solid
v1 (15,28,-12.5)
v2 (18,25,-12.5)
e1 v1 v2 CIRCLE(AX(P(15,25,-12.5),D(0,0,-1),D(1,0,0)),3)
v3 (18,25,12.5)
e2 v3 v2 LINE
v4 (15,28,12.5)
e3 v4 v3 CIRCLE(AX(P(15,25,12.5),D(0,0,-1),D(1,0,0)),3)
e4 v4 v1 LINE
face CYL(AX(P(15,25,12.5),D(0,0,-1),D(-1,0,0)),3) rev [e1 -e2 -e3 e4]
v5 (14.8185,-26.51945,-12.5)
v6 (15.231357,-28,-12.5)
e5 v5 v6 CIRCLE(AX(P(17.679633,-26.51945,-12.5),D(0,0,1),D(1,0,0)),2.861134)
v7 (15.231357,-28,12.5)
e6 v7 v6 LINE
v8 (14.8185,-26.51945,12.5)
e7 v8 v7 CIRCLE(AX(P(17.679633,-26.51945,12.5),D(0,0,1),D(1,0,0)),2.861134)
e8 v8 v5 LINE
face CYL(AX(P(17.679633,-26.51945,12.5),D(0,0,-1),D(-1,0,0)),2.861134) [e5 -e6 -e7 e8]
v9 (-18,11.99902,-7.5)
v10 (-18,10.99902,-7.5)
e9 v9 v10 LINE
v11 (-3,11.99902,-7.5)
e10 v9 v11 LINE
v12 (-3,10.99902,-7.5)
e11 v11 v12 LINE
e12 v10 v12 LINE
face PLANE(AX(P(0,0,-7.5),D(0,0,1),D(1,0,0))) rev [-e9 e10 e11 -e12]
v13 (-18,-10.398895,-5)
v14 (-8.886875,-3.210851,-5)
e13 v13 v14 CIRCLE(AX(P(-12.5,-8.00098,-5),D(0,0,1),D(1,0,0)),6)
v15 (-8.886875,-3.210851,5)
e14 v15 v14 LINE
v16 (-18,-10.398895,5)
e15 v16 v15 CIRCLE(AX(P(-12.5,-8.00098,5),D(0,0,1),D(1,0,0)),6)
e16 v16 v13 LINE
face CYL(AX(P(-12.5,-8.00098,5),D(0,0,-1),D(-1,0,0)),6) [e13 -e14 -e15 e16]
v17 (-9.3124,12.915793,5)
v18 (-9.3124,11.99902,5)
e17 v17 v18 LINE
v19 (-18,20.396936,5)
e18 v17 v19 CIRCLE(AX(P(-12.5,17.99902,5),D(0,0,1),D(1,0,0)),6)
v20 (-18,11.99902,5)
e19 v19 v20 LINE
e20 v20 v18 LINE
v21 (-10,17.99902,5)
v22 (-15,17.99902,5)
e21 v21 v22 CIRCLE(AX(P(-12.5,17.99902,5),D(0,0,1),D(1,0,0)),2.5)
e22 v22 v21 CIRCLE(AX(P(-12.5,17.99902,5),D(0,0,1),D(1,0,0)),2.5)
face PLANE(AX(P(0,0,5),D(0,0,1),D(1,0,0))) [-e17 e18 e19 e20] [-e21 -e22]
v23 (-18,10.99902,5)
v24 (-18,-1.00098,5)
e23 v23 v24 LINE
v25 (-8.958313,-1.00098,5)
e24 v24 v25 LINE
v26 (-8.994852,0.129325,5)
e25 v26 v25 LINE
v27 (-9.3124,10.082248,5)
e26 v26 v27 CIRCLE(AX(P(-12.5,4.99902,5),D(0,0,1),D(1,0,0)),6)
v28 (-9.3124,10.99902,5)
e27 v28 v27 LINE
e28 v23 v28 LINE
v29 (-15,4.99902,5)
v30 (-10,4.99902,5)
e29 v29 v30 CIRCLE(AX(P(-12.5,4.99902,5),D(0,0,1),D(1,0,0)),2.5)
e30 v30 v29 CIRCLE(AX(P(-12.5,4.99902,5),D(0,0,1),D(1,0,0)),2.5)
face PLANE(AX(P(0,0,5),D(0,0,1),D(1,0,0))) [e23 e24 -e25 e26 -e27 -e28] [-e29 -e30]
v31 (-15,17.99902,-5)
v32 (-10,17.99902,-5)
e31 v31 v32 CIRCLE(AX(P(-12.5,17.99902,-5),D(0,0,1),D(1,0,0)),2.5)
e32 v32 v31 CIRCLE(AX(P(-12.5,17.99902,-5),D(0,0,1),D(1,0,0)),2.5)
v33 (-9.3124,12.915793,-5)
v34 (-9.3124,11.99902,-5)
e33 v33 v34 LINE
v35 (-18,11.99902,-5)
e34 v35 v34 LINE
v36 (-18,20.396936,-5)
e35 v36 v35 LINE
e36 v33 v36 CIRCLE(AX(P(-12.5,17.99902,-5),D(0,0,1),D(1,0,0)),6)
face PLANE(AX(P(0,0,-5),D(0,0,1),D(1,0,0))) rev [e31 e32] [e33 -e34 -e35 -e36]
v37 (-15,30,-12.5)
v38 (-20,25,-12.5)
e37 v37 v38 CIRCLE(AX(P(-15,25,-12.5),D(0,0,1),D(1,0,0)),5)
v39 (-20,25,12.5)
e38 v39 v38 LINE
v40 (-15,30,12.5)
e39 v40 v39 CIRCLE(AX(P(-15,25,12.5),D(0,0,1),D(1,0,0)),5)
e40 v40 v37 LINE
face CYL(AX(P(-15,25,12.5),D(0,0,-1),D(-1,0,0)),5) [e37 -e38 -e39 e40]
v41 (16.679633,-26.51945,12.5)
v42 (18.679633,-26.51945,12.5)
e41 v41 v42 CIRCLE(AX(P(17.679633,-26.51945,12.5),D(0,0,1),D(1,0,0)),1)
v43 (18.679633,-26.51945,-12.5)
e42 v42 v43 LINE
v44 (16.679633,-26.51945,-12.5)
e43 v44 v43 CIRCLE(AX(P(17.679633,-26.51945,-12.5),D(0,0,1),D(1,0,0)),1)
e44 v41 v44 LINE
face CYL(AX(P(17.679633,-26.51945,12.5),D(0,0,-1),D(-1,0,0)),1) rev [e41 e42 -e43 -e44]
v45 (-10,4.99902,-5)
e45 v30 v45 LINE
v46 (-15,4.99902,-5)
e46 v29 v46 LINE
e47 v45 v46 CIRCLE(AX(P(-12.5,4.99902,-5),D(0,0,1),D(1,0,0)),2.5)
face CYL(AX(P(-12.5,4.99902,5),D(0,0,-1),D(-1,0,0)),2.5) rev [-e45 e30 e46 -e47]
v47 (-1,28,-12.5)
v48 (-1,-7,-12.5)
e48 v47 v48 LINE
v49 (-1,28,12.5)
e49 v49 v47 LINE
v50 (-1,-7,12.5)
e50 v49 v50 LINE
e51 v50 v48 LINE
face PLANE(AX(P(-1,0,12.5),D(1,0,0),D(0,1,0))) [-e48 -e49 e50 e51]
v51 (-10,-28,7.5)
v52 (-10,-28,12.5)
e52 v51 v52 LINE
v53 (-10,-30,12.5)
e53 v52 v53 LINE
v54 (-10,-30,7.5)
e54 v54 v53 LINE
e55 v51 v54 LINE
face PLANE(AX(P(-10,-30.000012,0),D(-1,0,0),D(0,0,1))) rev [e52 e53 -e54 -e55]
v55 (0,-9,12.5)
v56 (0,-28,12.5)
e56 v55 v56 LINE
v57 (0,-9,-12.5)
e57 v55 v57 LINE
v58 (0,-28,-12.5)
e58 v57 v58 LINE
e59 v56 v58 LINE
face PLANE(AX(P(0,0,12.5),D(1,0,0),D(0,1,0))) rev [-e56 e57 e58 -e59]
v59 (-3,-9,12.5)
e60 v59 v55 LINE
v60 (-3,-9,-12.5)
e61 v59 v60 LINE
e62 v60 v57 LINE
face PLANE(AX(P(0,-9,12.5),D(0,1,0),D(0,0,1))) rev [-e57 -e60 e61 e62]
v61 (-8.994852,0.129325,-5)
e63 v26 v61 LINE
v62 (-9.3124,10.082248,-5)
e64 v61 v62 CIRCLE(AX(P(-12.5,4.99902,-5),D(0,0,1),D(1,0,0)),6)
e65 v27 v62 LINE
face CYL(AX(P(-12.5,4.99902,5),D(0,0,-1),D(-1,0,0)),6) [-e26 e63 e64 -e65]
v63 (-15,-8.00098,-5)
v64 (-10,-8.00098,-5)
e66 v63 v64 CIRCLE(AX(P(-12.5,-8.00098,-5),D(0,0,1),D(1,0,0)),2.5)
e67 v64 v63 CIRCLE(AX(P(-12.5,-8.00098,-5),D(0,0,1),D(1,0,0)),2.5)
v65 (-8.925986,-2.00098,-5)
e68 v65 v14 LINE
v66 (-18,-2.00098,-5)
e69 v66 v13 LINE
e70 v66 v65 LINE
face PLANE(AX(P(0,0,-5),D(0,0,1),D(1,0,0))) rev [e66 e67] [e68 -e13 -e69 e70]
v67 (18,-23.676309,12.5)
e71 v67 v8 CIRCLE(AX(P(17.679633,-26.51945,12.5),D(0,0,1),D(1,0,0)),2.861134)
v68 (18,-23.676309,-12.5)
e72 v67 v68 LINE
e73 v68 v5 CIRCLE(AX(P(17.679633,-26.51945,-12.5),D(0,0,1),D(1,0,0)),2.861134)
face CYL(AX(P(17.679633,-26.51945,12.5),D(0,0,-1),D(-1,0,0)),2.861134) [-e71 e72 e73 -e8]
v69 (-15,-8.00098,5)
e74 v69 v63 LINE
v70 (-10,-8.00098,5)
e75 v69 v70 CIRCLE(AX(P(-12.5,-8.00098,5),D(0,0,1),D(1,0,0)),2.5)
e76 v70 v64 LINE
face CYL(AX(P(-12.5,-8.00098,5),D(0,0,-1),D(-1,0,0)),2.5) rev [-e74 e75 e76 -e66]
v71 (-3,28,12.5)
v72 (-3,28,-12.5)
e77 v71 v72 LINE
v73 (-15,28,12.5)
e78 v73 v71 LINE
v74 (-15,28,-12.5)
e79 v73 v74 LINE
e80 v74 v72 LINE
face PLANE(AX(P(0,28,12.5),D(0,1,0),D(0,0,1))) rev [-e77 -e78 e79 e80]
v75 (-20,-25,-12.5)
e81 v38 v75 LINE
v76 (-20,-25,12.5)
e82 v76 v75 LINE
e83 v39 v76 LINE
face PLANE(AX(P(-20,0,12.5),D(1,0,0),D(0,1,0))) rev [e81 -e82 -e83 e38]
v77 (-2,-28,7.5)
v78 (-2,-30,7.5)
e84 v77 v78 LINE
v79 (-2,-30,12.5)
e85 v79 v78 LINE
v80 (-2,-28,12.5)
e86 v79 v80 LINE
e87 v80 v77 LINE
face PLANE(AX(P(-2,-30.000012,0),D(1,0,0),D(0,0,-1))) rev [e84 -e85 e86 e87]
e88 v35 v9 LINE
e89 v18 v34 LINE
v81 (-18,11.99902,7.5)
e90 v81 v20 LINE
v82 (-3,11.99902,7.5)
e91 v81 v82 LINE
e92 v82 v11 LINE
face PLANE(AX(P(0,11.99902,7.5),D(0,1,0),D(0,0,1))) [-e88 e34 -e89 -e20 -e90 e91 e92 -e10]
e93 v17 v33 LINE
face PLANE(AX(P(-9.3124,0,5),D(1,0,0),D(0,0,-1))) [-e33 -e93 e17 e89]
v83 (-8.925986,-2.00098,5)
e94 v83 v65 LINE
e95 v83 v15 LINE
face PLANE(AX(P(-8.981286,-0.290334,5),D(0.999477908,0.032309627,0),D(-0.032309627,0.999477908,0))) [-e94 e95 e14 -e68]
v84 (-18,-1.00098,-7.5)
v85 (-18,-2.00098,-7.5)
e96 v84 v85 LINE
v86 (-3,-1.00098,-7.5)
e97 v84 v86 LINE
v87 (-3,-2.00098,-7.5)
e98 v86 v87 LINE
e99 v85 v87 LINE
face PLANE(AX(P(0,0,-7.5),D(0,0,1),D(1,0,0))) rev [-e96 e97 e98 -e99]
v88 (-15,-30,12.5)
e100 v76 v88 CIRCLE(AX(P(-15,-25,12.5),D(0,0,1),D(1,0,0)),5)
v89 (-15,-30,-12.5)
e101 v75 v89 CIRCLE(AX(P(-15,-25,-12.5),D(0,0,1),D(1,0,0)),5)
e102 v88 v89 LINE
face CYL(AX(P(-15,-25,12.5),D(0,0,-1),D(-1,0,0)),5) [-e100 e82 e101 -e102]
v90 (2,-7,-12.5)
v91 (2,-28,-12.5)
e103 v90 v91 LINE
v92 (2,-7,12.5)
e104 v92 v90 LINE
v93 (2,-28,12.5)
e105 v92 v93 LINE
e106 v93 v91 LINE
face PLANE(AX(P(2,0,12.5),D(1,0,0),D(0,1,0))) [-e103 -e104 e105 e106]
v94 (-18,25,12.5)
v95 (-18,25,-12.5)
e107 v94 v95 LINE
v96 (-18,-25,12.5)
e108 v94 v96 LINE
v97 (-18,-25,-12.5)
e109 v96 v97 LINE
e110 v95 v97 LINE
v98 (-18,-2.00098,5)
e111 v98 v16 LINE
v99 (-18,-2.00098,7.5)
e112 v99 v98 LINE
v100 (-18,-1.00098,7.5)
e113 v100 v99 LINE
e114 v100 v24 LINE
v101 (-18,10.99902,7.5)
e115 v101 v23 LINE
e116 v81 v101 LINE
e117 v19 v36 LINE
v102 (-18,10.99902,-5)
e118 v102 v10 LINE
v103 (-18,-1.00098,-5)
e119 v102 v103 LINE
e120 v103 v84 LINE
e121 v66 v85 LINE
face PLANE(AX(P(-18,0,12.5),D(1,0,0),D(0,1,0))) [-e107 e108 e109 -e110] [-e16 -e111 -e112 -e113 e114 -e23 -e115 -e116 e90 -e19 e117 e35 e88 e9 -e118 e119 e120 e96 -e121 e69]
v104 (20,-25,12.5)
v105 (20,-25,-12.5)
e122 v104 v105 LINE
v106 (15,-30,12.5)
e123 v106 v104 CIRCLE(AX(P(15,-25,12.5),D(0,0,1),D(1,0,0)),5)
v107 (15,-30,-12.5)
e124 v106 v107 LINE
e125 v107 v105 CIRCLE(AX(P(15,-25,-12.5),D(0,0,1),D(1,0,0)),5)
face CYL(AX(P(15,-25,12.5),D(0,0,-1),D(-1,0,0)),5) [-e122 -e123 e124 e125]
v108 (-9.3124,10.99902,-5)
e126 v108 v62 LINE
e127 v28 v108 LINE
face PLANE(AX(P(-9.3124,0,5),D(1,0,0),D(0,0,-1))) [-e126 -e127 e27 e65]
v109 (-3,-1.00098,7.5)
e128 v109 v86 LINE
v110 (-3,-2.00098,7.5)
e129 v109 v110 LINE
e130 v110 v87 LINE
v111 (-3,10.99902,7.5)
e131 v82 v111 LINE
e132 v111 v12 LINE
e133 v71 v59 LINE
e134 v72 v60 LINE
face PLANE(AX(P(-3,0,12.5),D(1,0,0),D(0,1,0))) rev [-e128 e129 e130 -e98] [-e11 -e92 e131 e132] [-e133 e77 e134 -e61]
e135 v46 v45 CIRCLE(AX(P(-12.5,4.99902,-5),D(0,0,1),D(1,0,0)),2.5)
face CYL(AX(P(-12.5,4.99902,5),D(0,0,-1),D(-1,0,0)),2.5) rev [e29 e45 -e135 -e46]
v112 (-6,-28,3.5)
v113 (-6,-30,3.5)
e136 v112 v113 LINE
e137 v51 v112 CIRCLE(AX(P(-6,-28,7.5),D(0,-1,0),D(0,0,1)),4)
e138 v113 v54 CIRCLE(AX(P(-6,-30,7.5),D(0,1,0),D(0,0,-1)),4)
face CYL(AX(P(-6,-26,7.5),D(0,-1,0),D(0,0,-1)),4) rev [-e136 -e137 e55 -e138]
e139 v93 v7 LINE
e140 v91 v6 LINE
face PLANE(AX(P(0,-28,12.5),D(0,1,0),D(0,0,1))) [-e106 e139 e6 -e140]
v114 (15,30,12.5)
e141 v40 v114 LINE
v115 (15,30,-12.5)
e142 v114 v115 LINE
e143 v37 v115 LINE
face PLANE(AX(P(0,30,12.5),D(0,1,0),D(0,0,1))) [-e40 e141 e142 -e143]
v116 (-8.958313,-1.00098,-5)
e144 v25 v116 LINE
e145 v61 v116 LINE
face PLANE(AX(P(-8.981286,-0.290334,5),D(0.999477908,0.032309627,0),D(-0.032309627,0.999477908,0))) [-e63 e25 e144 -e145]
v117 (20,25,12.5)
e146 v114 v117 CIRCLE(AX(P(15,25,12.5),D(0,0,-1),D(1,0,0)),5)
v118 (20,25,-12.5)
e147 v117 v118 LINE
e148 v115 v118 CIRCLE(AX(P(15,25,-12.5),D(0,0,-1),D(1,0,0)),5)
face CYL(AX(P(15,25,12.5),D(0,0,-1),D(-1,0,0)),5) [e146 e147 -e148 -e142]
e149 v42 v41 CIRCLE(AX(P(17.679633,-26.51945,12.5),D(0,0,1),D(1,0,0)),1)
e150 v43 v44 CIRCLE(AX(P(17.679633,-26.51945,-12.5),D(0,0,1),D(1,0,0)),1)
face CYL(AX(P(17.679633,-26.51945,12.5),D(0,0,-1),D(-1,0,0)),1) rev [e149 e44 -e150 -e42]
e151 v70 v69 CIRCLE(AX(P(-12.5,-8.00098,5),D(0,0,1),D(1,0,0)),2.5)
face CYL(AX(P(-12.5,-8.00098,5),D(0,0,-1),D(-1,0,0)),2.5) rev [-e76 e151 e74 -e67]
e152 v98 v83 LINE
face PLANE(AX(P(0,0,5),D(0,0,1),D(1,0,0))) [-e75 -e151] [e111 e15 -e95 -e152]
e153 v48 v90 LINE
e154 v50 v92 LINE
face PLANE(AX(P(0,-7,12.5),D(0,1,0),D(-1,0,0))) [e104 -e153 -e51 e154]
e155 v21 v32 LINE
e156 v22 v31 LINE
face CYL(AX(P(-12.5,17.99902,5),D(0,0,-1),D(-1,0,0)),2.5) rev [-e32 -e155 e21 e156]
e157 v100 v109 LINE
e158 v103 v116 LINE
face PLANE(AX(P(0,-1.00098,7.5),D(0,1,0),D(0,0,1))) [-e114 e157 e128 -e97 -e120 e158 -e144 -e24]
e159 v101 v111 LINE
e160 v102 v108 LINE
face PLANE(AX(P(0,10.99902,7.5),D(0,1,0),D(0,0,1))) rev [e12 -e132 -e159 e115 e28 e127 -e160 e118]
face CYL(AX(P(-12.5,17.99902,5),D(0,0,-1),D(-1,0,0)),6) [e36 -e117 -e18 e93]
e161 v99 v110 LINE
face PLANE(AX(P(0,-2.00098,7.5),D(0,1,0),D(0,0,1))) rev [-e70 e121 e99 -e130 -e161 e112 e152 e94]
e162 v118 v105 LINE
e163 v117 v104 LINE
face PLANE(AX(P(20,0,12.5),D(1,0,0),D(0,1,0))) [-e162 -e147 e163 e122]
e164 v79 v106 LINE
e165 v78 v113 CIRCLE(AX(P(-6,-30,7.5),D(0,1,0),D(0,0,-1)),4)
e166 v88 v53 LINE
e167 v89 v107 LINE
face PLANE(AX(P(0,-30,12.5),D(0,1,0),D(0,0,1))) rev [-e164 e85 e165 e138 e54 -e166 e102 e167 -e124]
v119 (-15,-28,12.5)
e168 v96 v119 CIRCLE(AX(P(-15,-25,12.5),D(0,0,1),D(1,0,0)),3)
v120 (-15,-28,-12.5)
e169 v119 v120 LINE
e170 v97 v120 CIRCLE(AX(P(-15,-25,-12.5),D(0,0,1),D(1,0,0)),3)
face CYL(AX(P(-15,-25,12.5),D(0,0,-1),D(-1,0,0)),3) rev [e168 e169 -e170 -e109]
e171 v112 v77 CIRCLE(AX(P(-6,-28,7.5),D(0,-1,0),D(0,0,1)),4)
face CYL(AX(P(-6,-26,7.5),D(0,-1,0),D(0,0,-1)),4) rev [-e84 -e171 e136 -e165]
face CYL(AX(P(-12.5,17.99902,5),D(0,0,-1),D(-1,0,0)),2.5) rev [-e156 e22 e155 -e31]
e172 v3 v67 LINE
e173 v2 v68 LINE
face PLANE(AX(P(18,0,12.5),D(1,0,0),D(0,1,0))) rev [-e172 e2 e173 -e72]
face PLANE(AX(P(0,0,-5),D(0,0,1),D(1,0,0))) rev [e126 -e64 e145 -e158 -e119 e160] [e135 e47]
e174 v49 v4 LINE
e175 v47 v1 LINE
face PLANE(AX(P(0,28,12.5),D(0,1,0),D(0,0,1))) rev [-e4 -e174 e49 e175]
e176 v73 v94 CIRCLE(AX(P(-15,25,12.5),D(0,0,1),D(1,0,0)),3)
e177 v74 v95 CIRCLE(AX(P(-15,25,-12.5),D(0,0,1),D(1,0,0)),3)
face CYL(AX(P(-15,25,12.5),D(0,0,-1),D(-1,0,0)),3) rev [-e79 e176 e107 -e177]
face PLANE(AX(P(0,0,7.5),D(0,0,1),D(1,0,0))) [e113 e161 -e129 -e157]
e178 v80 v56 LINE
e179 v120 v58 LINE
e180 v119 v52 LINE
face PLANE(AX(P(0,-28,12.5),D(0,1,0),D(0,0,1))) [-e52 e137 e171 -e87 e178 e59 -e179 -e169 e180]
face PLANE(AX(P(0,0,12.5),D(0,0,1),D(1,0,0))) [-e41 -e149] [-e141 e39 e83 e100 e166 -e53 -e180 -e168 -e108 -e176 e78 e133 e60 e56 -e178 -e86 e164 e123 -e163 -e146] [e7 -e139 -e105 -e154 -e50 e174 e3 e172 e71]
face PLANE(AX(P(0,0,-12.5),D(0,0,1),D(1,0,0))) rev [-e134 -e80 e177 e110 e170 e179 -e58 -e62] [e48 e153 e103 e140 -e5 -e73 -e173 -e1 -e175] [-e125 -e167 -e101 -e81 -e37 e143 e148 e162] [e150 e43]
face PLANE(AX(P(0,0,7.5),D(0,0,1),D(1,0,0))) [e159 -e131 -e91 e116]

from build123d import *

# Parameters (mm, degrees)
BOX_PROFILE_SKETCH_R      = 1
BOX_SHELL_25MM_DEPTH      = 12.5
PARTITION_WALL_15MM_DEPTH = 7.5
SKETCH1_5_R               = 2.5
PARTITION_WALL_10MM_DEPTH = 5
NOTCH_CUT_4MM_DEPTH       = 65.468984791
NOTCH_CUT_4MM_DEPTH_BACK  = 4


with BuildPart() as part:
    # Box Profile Sketch → Box Shell 25mm (new, symmetric)
    with BuildSketch(Plane.XY):
        with BuildLine():
            Line((15, 30), (-15, 30))
            ThreePointArc((-15, 30), (-18.535533906, 28.535533906), (-20, 25))
            Line((-20, 25), (-20, -25))
            ThreePointArc((-20, -25), (-18.535533906, -28.535533906), (-15, -30))
            Line((-15, -30), (-7, -30))
            Line((-7, -30), (-3, -30))
            Line((-3, -30), (15, -30))
            ThreePointArc((15, -30), (18.535533906, -28.535533906), (20, -25))
            Line((20, -25), (20, 25))
            ThreePointArc((20, 25), (18.535533906, 28.535533906), (15, 30))
        make_face()
        with BuildLine():
            ThreePointArc((-18, 25), (-17.121320344, 27.121320344), (-15, 28))
            Line((-15, 28), (-3, 28))
            Line((-3, 28), (-3, 11.9990204))
            Line((-3, 11.9990204), (-3, 10.9990204))
            Line((-3, 10.9990204), (-3, -1.0009796))
            Line((-3, -1.0009796), (-3, -2.0009796))
            Line((-3, -2.0009796), (-3, -9))
            Line((-3, -9), (0, -9))
            Line((0, -9), (0, -28))
            Line((0, -28), (-3, -28))
            Line((-3, -28), (-7, -28))
            Line((-7, -28), (-15, -28))
            ThreePointArc((-15, -28), (-17.121320344, -27.121320344), (-18, -25))
            Line((-18, -25), (-18, -10.398895362))
            Line((-18, -10.398895362), (-18, -2.0009796))
            Line((-18, -2.0009796), (-18, -1.0009796))
            Line((-18, -1.0009796), (-18, 10.9990204))
            Line((-18, 10.9990204), (-18, 11.9990204))
            Line((-18, 11.9990204), (-18, 20.396936162))
            Line((-18, 20.396936162), (-18, 25))
        make_face(mode=Mode.SUBTRACT)
        with Locations((17.67963323, -26.519449845)):
            Circle(BOX_PROFILE_SKETCH_R, mode=Mode.SUBTRACT)
        with BuildLine():
            ThreePointArc((15, 28), (17.121320344, 27.121320344), (18, 25))
            Line((18, 25), (18, -23.676308898))
            ThreePointArc((18, -23.676308898), (15.270156966, -24.976559879), (15.23135699, -28))
            Line((15.23135699, -28), (2, -28))
            Line((2, -28), (2, -7))
            Line((2, -7), (-1, -7))
            Line((-1, -7), (-1, 28))
            Line((-1, 28), (15, 28))
        make_face(mode=Mode.SUBTRACT)
    extrude(amount=BOX_SHELL_25MM_DEPTH, both=True)

    # Sketch1_3 → Partition Wall 15mm (add, symmetric)
    with BuildSketch(Plane.XY):
        Polygon((-3, -2.0009796), (-3, -1.0009796), (-8.958312837, -1.0009796), (-18, -1.0009796), (-18, -2.0009796), (-8.925986332, -2.0009796), align=None)
        Polygon((-3, 10.9990204), (-3, 11.9990204), (-9.312399857, 11.9990204), (-18, 11.9990204), (-18, 10.9990204), (-9.312399857, 10.9990204), align=None)
    extrude(amount=PARTITION_WALL_15MM_DEPTH, both=True)

    # Sketch1_5 → Partition Wall 10mm (add, symmetric)
    # profile 1 of 3: a face of its own
    with BuildSketch(Plane.XY):
        with BuildLine():
            ThreePointArc((-9.312399857, 12.915792555), (-8.584814731, 22.545593209), (-18, 20.396936162))
            Line((-18, 20.396936162), (-18, 11.9990204))
            Line((-18, 11.9990204), (-9.312399857, 11.9990204))
            Line((-9.312399857, 11.9990204), (-9.312399857, 12.915792555))
        make_face()
        with Locations((-12.5, 17.9990204)):
            Circle(SKETCH1_5_R, mode=Mode.SUBTRACT)
    # profile 2 of 3: a face of its own
    with BuildSketch(Plane.XY):
        with BuildLine():
            Line((-9.312399857, 10.082248245), (-9.312399857, 10.9990204))
            Line((-9.312399857, 10.9990204), (-18, 10.9990204))
            Line((-18, 10.9990204), (-18, -1.0009796))
            Line((-18, -1.0009796), (-8.958312837, -1.0009796))
            Line((-8.958312837, -1.0009796), (-8.994851629, 0.129324835))
            ThreePointArc((-8.994851629, 0.129324835), (-6.503051462, 5.190353168), (-9.312399857, 10.082248245))
        make_face()
        with Locations((-12.5, 4.9990204)):
            Circle(SKETCH1_5_R, mode=Mode.SUBTRACT)
    # profile 3 of 3: a face of its own
    with BuildSketch(Plane.XY):
        with BuildLine():
            Line((-8.886875414, -3.210851133), (-8.925986332, -2.0009796))
            Line((-8.925986332, -2.0009796), (-18, -2.0009796))
            Line((-18, -2.0009796), (-18, -10.398895362))
            ThreePointArc((-18, -10.398895362), (-8.784213453, -12.71191691), (-8.886875414, -3.210851133))
        make_face()
        with Locations((-12.5, -8.0009796)):
            Circle(SKETCH1_5_R, mode=Mode.SUBTRACT)
    extrude(amount=PARTITION_WALL_10MM_DEPTH, both=True)

    # Notch Sketch → Notch Cut 4mm (cut, two sides: drawn at the far end of the back side and taken through both)
    with BuildSketch(Plane.XZ.offset(30).offset(-NOTCH_CUT_4MM_DEPTH_BACK)):
        with BuildLine():
            Line((-2, 7.5), (-2, 12.5))
            Line((-2, 12.5), (-10, 12.5))
            Line((-10, 12.5), (-10, 7.5))
            ThreePointArc((-10, 7.5), (-6, 3.5), (-2, 7.5))
        make_face()
    extrude(amount=NOTCH_CUT_4MM_DEPTH + NOTCH_CUT_4MM_DEPTH_BACK, mode=Mode.SUBTRACT)


solid = part.part
